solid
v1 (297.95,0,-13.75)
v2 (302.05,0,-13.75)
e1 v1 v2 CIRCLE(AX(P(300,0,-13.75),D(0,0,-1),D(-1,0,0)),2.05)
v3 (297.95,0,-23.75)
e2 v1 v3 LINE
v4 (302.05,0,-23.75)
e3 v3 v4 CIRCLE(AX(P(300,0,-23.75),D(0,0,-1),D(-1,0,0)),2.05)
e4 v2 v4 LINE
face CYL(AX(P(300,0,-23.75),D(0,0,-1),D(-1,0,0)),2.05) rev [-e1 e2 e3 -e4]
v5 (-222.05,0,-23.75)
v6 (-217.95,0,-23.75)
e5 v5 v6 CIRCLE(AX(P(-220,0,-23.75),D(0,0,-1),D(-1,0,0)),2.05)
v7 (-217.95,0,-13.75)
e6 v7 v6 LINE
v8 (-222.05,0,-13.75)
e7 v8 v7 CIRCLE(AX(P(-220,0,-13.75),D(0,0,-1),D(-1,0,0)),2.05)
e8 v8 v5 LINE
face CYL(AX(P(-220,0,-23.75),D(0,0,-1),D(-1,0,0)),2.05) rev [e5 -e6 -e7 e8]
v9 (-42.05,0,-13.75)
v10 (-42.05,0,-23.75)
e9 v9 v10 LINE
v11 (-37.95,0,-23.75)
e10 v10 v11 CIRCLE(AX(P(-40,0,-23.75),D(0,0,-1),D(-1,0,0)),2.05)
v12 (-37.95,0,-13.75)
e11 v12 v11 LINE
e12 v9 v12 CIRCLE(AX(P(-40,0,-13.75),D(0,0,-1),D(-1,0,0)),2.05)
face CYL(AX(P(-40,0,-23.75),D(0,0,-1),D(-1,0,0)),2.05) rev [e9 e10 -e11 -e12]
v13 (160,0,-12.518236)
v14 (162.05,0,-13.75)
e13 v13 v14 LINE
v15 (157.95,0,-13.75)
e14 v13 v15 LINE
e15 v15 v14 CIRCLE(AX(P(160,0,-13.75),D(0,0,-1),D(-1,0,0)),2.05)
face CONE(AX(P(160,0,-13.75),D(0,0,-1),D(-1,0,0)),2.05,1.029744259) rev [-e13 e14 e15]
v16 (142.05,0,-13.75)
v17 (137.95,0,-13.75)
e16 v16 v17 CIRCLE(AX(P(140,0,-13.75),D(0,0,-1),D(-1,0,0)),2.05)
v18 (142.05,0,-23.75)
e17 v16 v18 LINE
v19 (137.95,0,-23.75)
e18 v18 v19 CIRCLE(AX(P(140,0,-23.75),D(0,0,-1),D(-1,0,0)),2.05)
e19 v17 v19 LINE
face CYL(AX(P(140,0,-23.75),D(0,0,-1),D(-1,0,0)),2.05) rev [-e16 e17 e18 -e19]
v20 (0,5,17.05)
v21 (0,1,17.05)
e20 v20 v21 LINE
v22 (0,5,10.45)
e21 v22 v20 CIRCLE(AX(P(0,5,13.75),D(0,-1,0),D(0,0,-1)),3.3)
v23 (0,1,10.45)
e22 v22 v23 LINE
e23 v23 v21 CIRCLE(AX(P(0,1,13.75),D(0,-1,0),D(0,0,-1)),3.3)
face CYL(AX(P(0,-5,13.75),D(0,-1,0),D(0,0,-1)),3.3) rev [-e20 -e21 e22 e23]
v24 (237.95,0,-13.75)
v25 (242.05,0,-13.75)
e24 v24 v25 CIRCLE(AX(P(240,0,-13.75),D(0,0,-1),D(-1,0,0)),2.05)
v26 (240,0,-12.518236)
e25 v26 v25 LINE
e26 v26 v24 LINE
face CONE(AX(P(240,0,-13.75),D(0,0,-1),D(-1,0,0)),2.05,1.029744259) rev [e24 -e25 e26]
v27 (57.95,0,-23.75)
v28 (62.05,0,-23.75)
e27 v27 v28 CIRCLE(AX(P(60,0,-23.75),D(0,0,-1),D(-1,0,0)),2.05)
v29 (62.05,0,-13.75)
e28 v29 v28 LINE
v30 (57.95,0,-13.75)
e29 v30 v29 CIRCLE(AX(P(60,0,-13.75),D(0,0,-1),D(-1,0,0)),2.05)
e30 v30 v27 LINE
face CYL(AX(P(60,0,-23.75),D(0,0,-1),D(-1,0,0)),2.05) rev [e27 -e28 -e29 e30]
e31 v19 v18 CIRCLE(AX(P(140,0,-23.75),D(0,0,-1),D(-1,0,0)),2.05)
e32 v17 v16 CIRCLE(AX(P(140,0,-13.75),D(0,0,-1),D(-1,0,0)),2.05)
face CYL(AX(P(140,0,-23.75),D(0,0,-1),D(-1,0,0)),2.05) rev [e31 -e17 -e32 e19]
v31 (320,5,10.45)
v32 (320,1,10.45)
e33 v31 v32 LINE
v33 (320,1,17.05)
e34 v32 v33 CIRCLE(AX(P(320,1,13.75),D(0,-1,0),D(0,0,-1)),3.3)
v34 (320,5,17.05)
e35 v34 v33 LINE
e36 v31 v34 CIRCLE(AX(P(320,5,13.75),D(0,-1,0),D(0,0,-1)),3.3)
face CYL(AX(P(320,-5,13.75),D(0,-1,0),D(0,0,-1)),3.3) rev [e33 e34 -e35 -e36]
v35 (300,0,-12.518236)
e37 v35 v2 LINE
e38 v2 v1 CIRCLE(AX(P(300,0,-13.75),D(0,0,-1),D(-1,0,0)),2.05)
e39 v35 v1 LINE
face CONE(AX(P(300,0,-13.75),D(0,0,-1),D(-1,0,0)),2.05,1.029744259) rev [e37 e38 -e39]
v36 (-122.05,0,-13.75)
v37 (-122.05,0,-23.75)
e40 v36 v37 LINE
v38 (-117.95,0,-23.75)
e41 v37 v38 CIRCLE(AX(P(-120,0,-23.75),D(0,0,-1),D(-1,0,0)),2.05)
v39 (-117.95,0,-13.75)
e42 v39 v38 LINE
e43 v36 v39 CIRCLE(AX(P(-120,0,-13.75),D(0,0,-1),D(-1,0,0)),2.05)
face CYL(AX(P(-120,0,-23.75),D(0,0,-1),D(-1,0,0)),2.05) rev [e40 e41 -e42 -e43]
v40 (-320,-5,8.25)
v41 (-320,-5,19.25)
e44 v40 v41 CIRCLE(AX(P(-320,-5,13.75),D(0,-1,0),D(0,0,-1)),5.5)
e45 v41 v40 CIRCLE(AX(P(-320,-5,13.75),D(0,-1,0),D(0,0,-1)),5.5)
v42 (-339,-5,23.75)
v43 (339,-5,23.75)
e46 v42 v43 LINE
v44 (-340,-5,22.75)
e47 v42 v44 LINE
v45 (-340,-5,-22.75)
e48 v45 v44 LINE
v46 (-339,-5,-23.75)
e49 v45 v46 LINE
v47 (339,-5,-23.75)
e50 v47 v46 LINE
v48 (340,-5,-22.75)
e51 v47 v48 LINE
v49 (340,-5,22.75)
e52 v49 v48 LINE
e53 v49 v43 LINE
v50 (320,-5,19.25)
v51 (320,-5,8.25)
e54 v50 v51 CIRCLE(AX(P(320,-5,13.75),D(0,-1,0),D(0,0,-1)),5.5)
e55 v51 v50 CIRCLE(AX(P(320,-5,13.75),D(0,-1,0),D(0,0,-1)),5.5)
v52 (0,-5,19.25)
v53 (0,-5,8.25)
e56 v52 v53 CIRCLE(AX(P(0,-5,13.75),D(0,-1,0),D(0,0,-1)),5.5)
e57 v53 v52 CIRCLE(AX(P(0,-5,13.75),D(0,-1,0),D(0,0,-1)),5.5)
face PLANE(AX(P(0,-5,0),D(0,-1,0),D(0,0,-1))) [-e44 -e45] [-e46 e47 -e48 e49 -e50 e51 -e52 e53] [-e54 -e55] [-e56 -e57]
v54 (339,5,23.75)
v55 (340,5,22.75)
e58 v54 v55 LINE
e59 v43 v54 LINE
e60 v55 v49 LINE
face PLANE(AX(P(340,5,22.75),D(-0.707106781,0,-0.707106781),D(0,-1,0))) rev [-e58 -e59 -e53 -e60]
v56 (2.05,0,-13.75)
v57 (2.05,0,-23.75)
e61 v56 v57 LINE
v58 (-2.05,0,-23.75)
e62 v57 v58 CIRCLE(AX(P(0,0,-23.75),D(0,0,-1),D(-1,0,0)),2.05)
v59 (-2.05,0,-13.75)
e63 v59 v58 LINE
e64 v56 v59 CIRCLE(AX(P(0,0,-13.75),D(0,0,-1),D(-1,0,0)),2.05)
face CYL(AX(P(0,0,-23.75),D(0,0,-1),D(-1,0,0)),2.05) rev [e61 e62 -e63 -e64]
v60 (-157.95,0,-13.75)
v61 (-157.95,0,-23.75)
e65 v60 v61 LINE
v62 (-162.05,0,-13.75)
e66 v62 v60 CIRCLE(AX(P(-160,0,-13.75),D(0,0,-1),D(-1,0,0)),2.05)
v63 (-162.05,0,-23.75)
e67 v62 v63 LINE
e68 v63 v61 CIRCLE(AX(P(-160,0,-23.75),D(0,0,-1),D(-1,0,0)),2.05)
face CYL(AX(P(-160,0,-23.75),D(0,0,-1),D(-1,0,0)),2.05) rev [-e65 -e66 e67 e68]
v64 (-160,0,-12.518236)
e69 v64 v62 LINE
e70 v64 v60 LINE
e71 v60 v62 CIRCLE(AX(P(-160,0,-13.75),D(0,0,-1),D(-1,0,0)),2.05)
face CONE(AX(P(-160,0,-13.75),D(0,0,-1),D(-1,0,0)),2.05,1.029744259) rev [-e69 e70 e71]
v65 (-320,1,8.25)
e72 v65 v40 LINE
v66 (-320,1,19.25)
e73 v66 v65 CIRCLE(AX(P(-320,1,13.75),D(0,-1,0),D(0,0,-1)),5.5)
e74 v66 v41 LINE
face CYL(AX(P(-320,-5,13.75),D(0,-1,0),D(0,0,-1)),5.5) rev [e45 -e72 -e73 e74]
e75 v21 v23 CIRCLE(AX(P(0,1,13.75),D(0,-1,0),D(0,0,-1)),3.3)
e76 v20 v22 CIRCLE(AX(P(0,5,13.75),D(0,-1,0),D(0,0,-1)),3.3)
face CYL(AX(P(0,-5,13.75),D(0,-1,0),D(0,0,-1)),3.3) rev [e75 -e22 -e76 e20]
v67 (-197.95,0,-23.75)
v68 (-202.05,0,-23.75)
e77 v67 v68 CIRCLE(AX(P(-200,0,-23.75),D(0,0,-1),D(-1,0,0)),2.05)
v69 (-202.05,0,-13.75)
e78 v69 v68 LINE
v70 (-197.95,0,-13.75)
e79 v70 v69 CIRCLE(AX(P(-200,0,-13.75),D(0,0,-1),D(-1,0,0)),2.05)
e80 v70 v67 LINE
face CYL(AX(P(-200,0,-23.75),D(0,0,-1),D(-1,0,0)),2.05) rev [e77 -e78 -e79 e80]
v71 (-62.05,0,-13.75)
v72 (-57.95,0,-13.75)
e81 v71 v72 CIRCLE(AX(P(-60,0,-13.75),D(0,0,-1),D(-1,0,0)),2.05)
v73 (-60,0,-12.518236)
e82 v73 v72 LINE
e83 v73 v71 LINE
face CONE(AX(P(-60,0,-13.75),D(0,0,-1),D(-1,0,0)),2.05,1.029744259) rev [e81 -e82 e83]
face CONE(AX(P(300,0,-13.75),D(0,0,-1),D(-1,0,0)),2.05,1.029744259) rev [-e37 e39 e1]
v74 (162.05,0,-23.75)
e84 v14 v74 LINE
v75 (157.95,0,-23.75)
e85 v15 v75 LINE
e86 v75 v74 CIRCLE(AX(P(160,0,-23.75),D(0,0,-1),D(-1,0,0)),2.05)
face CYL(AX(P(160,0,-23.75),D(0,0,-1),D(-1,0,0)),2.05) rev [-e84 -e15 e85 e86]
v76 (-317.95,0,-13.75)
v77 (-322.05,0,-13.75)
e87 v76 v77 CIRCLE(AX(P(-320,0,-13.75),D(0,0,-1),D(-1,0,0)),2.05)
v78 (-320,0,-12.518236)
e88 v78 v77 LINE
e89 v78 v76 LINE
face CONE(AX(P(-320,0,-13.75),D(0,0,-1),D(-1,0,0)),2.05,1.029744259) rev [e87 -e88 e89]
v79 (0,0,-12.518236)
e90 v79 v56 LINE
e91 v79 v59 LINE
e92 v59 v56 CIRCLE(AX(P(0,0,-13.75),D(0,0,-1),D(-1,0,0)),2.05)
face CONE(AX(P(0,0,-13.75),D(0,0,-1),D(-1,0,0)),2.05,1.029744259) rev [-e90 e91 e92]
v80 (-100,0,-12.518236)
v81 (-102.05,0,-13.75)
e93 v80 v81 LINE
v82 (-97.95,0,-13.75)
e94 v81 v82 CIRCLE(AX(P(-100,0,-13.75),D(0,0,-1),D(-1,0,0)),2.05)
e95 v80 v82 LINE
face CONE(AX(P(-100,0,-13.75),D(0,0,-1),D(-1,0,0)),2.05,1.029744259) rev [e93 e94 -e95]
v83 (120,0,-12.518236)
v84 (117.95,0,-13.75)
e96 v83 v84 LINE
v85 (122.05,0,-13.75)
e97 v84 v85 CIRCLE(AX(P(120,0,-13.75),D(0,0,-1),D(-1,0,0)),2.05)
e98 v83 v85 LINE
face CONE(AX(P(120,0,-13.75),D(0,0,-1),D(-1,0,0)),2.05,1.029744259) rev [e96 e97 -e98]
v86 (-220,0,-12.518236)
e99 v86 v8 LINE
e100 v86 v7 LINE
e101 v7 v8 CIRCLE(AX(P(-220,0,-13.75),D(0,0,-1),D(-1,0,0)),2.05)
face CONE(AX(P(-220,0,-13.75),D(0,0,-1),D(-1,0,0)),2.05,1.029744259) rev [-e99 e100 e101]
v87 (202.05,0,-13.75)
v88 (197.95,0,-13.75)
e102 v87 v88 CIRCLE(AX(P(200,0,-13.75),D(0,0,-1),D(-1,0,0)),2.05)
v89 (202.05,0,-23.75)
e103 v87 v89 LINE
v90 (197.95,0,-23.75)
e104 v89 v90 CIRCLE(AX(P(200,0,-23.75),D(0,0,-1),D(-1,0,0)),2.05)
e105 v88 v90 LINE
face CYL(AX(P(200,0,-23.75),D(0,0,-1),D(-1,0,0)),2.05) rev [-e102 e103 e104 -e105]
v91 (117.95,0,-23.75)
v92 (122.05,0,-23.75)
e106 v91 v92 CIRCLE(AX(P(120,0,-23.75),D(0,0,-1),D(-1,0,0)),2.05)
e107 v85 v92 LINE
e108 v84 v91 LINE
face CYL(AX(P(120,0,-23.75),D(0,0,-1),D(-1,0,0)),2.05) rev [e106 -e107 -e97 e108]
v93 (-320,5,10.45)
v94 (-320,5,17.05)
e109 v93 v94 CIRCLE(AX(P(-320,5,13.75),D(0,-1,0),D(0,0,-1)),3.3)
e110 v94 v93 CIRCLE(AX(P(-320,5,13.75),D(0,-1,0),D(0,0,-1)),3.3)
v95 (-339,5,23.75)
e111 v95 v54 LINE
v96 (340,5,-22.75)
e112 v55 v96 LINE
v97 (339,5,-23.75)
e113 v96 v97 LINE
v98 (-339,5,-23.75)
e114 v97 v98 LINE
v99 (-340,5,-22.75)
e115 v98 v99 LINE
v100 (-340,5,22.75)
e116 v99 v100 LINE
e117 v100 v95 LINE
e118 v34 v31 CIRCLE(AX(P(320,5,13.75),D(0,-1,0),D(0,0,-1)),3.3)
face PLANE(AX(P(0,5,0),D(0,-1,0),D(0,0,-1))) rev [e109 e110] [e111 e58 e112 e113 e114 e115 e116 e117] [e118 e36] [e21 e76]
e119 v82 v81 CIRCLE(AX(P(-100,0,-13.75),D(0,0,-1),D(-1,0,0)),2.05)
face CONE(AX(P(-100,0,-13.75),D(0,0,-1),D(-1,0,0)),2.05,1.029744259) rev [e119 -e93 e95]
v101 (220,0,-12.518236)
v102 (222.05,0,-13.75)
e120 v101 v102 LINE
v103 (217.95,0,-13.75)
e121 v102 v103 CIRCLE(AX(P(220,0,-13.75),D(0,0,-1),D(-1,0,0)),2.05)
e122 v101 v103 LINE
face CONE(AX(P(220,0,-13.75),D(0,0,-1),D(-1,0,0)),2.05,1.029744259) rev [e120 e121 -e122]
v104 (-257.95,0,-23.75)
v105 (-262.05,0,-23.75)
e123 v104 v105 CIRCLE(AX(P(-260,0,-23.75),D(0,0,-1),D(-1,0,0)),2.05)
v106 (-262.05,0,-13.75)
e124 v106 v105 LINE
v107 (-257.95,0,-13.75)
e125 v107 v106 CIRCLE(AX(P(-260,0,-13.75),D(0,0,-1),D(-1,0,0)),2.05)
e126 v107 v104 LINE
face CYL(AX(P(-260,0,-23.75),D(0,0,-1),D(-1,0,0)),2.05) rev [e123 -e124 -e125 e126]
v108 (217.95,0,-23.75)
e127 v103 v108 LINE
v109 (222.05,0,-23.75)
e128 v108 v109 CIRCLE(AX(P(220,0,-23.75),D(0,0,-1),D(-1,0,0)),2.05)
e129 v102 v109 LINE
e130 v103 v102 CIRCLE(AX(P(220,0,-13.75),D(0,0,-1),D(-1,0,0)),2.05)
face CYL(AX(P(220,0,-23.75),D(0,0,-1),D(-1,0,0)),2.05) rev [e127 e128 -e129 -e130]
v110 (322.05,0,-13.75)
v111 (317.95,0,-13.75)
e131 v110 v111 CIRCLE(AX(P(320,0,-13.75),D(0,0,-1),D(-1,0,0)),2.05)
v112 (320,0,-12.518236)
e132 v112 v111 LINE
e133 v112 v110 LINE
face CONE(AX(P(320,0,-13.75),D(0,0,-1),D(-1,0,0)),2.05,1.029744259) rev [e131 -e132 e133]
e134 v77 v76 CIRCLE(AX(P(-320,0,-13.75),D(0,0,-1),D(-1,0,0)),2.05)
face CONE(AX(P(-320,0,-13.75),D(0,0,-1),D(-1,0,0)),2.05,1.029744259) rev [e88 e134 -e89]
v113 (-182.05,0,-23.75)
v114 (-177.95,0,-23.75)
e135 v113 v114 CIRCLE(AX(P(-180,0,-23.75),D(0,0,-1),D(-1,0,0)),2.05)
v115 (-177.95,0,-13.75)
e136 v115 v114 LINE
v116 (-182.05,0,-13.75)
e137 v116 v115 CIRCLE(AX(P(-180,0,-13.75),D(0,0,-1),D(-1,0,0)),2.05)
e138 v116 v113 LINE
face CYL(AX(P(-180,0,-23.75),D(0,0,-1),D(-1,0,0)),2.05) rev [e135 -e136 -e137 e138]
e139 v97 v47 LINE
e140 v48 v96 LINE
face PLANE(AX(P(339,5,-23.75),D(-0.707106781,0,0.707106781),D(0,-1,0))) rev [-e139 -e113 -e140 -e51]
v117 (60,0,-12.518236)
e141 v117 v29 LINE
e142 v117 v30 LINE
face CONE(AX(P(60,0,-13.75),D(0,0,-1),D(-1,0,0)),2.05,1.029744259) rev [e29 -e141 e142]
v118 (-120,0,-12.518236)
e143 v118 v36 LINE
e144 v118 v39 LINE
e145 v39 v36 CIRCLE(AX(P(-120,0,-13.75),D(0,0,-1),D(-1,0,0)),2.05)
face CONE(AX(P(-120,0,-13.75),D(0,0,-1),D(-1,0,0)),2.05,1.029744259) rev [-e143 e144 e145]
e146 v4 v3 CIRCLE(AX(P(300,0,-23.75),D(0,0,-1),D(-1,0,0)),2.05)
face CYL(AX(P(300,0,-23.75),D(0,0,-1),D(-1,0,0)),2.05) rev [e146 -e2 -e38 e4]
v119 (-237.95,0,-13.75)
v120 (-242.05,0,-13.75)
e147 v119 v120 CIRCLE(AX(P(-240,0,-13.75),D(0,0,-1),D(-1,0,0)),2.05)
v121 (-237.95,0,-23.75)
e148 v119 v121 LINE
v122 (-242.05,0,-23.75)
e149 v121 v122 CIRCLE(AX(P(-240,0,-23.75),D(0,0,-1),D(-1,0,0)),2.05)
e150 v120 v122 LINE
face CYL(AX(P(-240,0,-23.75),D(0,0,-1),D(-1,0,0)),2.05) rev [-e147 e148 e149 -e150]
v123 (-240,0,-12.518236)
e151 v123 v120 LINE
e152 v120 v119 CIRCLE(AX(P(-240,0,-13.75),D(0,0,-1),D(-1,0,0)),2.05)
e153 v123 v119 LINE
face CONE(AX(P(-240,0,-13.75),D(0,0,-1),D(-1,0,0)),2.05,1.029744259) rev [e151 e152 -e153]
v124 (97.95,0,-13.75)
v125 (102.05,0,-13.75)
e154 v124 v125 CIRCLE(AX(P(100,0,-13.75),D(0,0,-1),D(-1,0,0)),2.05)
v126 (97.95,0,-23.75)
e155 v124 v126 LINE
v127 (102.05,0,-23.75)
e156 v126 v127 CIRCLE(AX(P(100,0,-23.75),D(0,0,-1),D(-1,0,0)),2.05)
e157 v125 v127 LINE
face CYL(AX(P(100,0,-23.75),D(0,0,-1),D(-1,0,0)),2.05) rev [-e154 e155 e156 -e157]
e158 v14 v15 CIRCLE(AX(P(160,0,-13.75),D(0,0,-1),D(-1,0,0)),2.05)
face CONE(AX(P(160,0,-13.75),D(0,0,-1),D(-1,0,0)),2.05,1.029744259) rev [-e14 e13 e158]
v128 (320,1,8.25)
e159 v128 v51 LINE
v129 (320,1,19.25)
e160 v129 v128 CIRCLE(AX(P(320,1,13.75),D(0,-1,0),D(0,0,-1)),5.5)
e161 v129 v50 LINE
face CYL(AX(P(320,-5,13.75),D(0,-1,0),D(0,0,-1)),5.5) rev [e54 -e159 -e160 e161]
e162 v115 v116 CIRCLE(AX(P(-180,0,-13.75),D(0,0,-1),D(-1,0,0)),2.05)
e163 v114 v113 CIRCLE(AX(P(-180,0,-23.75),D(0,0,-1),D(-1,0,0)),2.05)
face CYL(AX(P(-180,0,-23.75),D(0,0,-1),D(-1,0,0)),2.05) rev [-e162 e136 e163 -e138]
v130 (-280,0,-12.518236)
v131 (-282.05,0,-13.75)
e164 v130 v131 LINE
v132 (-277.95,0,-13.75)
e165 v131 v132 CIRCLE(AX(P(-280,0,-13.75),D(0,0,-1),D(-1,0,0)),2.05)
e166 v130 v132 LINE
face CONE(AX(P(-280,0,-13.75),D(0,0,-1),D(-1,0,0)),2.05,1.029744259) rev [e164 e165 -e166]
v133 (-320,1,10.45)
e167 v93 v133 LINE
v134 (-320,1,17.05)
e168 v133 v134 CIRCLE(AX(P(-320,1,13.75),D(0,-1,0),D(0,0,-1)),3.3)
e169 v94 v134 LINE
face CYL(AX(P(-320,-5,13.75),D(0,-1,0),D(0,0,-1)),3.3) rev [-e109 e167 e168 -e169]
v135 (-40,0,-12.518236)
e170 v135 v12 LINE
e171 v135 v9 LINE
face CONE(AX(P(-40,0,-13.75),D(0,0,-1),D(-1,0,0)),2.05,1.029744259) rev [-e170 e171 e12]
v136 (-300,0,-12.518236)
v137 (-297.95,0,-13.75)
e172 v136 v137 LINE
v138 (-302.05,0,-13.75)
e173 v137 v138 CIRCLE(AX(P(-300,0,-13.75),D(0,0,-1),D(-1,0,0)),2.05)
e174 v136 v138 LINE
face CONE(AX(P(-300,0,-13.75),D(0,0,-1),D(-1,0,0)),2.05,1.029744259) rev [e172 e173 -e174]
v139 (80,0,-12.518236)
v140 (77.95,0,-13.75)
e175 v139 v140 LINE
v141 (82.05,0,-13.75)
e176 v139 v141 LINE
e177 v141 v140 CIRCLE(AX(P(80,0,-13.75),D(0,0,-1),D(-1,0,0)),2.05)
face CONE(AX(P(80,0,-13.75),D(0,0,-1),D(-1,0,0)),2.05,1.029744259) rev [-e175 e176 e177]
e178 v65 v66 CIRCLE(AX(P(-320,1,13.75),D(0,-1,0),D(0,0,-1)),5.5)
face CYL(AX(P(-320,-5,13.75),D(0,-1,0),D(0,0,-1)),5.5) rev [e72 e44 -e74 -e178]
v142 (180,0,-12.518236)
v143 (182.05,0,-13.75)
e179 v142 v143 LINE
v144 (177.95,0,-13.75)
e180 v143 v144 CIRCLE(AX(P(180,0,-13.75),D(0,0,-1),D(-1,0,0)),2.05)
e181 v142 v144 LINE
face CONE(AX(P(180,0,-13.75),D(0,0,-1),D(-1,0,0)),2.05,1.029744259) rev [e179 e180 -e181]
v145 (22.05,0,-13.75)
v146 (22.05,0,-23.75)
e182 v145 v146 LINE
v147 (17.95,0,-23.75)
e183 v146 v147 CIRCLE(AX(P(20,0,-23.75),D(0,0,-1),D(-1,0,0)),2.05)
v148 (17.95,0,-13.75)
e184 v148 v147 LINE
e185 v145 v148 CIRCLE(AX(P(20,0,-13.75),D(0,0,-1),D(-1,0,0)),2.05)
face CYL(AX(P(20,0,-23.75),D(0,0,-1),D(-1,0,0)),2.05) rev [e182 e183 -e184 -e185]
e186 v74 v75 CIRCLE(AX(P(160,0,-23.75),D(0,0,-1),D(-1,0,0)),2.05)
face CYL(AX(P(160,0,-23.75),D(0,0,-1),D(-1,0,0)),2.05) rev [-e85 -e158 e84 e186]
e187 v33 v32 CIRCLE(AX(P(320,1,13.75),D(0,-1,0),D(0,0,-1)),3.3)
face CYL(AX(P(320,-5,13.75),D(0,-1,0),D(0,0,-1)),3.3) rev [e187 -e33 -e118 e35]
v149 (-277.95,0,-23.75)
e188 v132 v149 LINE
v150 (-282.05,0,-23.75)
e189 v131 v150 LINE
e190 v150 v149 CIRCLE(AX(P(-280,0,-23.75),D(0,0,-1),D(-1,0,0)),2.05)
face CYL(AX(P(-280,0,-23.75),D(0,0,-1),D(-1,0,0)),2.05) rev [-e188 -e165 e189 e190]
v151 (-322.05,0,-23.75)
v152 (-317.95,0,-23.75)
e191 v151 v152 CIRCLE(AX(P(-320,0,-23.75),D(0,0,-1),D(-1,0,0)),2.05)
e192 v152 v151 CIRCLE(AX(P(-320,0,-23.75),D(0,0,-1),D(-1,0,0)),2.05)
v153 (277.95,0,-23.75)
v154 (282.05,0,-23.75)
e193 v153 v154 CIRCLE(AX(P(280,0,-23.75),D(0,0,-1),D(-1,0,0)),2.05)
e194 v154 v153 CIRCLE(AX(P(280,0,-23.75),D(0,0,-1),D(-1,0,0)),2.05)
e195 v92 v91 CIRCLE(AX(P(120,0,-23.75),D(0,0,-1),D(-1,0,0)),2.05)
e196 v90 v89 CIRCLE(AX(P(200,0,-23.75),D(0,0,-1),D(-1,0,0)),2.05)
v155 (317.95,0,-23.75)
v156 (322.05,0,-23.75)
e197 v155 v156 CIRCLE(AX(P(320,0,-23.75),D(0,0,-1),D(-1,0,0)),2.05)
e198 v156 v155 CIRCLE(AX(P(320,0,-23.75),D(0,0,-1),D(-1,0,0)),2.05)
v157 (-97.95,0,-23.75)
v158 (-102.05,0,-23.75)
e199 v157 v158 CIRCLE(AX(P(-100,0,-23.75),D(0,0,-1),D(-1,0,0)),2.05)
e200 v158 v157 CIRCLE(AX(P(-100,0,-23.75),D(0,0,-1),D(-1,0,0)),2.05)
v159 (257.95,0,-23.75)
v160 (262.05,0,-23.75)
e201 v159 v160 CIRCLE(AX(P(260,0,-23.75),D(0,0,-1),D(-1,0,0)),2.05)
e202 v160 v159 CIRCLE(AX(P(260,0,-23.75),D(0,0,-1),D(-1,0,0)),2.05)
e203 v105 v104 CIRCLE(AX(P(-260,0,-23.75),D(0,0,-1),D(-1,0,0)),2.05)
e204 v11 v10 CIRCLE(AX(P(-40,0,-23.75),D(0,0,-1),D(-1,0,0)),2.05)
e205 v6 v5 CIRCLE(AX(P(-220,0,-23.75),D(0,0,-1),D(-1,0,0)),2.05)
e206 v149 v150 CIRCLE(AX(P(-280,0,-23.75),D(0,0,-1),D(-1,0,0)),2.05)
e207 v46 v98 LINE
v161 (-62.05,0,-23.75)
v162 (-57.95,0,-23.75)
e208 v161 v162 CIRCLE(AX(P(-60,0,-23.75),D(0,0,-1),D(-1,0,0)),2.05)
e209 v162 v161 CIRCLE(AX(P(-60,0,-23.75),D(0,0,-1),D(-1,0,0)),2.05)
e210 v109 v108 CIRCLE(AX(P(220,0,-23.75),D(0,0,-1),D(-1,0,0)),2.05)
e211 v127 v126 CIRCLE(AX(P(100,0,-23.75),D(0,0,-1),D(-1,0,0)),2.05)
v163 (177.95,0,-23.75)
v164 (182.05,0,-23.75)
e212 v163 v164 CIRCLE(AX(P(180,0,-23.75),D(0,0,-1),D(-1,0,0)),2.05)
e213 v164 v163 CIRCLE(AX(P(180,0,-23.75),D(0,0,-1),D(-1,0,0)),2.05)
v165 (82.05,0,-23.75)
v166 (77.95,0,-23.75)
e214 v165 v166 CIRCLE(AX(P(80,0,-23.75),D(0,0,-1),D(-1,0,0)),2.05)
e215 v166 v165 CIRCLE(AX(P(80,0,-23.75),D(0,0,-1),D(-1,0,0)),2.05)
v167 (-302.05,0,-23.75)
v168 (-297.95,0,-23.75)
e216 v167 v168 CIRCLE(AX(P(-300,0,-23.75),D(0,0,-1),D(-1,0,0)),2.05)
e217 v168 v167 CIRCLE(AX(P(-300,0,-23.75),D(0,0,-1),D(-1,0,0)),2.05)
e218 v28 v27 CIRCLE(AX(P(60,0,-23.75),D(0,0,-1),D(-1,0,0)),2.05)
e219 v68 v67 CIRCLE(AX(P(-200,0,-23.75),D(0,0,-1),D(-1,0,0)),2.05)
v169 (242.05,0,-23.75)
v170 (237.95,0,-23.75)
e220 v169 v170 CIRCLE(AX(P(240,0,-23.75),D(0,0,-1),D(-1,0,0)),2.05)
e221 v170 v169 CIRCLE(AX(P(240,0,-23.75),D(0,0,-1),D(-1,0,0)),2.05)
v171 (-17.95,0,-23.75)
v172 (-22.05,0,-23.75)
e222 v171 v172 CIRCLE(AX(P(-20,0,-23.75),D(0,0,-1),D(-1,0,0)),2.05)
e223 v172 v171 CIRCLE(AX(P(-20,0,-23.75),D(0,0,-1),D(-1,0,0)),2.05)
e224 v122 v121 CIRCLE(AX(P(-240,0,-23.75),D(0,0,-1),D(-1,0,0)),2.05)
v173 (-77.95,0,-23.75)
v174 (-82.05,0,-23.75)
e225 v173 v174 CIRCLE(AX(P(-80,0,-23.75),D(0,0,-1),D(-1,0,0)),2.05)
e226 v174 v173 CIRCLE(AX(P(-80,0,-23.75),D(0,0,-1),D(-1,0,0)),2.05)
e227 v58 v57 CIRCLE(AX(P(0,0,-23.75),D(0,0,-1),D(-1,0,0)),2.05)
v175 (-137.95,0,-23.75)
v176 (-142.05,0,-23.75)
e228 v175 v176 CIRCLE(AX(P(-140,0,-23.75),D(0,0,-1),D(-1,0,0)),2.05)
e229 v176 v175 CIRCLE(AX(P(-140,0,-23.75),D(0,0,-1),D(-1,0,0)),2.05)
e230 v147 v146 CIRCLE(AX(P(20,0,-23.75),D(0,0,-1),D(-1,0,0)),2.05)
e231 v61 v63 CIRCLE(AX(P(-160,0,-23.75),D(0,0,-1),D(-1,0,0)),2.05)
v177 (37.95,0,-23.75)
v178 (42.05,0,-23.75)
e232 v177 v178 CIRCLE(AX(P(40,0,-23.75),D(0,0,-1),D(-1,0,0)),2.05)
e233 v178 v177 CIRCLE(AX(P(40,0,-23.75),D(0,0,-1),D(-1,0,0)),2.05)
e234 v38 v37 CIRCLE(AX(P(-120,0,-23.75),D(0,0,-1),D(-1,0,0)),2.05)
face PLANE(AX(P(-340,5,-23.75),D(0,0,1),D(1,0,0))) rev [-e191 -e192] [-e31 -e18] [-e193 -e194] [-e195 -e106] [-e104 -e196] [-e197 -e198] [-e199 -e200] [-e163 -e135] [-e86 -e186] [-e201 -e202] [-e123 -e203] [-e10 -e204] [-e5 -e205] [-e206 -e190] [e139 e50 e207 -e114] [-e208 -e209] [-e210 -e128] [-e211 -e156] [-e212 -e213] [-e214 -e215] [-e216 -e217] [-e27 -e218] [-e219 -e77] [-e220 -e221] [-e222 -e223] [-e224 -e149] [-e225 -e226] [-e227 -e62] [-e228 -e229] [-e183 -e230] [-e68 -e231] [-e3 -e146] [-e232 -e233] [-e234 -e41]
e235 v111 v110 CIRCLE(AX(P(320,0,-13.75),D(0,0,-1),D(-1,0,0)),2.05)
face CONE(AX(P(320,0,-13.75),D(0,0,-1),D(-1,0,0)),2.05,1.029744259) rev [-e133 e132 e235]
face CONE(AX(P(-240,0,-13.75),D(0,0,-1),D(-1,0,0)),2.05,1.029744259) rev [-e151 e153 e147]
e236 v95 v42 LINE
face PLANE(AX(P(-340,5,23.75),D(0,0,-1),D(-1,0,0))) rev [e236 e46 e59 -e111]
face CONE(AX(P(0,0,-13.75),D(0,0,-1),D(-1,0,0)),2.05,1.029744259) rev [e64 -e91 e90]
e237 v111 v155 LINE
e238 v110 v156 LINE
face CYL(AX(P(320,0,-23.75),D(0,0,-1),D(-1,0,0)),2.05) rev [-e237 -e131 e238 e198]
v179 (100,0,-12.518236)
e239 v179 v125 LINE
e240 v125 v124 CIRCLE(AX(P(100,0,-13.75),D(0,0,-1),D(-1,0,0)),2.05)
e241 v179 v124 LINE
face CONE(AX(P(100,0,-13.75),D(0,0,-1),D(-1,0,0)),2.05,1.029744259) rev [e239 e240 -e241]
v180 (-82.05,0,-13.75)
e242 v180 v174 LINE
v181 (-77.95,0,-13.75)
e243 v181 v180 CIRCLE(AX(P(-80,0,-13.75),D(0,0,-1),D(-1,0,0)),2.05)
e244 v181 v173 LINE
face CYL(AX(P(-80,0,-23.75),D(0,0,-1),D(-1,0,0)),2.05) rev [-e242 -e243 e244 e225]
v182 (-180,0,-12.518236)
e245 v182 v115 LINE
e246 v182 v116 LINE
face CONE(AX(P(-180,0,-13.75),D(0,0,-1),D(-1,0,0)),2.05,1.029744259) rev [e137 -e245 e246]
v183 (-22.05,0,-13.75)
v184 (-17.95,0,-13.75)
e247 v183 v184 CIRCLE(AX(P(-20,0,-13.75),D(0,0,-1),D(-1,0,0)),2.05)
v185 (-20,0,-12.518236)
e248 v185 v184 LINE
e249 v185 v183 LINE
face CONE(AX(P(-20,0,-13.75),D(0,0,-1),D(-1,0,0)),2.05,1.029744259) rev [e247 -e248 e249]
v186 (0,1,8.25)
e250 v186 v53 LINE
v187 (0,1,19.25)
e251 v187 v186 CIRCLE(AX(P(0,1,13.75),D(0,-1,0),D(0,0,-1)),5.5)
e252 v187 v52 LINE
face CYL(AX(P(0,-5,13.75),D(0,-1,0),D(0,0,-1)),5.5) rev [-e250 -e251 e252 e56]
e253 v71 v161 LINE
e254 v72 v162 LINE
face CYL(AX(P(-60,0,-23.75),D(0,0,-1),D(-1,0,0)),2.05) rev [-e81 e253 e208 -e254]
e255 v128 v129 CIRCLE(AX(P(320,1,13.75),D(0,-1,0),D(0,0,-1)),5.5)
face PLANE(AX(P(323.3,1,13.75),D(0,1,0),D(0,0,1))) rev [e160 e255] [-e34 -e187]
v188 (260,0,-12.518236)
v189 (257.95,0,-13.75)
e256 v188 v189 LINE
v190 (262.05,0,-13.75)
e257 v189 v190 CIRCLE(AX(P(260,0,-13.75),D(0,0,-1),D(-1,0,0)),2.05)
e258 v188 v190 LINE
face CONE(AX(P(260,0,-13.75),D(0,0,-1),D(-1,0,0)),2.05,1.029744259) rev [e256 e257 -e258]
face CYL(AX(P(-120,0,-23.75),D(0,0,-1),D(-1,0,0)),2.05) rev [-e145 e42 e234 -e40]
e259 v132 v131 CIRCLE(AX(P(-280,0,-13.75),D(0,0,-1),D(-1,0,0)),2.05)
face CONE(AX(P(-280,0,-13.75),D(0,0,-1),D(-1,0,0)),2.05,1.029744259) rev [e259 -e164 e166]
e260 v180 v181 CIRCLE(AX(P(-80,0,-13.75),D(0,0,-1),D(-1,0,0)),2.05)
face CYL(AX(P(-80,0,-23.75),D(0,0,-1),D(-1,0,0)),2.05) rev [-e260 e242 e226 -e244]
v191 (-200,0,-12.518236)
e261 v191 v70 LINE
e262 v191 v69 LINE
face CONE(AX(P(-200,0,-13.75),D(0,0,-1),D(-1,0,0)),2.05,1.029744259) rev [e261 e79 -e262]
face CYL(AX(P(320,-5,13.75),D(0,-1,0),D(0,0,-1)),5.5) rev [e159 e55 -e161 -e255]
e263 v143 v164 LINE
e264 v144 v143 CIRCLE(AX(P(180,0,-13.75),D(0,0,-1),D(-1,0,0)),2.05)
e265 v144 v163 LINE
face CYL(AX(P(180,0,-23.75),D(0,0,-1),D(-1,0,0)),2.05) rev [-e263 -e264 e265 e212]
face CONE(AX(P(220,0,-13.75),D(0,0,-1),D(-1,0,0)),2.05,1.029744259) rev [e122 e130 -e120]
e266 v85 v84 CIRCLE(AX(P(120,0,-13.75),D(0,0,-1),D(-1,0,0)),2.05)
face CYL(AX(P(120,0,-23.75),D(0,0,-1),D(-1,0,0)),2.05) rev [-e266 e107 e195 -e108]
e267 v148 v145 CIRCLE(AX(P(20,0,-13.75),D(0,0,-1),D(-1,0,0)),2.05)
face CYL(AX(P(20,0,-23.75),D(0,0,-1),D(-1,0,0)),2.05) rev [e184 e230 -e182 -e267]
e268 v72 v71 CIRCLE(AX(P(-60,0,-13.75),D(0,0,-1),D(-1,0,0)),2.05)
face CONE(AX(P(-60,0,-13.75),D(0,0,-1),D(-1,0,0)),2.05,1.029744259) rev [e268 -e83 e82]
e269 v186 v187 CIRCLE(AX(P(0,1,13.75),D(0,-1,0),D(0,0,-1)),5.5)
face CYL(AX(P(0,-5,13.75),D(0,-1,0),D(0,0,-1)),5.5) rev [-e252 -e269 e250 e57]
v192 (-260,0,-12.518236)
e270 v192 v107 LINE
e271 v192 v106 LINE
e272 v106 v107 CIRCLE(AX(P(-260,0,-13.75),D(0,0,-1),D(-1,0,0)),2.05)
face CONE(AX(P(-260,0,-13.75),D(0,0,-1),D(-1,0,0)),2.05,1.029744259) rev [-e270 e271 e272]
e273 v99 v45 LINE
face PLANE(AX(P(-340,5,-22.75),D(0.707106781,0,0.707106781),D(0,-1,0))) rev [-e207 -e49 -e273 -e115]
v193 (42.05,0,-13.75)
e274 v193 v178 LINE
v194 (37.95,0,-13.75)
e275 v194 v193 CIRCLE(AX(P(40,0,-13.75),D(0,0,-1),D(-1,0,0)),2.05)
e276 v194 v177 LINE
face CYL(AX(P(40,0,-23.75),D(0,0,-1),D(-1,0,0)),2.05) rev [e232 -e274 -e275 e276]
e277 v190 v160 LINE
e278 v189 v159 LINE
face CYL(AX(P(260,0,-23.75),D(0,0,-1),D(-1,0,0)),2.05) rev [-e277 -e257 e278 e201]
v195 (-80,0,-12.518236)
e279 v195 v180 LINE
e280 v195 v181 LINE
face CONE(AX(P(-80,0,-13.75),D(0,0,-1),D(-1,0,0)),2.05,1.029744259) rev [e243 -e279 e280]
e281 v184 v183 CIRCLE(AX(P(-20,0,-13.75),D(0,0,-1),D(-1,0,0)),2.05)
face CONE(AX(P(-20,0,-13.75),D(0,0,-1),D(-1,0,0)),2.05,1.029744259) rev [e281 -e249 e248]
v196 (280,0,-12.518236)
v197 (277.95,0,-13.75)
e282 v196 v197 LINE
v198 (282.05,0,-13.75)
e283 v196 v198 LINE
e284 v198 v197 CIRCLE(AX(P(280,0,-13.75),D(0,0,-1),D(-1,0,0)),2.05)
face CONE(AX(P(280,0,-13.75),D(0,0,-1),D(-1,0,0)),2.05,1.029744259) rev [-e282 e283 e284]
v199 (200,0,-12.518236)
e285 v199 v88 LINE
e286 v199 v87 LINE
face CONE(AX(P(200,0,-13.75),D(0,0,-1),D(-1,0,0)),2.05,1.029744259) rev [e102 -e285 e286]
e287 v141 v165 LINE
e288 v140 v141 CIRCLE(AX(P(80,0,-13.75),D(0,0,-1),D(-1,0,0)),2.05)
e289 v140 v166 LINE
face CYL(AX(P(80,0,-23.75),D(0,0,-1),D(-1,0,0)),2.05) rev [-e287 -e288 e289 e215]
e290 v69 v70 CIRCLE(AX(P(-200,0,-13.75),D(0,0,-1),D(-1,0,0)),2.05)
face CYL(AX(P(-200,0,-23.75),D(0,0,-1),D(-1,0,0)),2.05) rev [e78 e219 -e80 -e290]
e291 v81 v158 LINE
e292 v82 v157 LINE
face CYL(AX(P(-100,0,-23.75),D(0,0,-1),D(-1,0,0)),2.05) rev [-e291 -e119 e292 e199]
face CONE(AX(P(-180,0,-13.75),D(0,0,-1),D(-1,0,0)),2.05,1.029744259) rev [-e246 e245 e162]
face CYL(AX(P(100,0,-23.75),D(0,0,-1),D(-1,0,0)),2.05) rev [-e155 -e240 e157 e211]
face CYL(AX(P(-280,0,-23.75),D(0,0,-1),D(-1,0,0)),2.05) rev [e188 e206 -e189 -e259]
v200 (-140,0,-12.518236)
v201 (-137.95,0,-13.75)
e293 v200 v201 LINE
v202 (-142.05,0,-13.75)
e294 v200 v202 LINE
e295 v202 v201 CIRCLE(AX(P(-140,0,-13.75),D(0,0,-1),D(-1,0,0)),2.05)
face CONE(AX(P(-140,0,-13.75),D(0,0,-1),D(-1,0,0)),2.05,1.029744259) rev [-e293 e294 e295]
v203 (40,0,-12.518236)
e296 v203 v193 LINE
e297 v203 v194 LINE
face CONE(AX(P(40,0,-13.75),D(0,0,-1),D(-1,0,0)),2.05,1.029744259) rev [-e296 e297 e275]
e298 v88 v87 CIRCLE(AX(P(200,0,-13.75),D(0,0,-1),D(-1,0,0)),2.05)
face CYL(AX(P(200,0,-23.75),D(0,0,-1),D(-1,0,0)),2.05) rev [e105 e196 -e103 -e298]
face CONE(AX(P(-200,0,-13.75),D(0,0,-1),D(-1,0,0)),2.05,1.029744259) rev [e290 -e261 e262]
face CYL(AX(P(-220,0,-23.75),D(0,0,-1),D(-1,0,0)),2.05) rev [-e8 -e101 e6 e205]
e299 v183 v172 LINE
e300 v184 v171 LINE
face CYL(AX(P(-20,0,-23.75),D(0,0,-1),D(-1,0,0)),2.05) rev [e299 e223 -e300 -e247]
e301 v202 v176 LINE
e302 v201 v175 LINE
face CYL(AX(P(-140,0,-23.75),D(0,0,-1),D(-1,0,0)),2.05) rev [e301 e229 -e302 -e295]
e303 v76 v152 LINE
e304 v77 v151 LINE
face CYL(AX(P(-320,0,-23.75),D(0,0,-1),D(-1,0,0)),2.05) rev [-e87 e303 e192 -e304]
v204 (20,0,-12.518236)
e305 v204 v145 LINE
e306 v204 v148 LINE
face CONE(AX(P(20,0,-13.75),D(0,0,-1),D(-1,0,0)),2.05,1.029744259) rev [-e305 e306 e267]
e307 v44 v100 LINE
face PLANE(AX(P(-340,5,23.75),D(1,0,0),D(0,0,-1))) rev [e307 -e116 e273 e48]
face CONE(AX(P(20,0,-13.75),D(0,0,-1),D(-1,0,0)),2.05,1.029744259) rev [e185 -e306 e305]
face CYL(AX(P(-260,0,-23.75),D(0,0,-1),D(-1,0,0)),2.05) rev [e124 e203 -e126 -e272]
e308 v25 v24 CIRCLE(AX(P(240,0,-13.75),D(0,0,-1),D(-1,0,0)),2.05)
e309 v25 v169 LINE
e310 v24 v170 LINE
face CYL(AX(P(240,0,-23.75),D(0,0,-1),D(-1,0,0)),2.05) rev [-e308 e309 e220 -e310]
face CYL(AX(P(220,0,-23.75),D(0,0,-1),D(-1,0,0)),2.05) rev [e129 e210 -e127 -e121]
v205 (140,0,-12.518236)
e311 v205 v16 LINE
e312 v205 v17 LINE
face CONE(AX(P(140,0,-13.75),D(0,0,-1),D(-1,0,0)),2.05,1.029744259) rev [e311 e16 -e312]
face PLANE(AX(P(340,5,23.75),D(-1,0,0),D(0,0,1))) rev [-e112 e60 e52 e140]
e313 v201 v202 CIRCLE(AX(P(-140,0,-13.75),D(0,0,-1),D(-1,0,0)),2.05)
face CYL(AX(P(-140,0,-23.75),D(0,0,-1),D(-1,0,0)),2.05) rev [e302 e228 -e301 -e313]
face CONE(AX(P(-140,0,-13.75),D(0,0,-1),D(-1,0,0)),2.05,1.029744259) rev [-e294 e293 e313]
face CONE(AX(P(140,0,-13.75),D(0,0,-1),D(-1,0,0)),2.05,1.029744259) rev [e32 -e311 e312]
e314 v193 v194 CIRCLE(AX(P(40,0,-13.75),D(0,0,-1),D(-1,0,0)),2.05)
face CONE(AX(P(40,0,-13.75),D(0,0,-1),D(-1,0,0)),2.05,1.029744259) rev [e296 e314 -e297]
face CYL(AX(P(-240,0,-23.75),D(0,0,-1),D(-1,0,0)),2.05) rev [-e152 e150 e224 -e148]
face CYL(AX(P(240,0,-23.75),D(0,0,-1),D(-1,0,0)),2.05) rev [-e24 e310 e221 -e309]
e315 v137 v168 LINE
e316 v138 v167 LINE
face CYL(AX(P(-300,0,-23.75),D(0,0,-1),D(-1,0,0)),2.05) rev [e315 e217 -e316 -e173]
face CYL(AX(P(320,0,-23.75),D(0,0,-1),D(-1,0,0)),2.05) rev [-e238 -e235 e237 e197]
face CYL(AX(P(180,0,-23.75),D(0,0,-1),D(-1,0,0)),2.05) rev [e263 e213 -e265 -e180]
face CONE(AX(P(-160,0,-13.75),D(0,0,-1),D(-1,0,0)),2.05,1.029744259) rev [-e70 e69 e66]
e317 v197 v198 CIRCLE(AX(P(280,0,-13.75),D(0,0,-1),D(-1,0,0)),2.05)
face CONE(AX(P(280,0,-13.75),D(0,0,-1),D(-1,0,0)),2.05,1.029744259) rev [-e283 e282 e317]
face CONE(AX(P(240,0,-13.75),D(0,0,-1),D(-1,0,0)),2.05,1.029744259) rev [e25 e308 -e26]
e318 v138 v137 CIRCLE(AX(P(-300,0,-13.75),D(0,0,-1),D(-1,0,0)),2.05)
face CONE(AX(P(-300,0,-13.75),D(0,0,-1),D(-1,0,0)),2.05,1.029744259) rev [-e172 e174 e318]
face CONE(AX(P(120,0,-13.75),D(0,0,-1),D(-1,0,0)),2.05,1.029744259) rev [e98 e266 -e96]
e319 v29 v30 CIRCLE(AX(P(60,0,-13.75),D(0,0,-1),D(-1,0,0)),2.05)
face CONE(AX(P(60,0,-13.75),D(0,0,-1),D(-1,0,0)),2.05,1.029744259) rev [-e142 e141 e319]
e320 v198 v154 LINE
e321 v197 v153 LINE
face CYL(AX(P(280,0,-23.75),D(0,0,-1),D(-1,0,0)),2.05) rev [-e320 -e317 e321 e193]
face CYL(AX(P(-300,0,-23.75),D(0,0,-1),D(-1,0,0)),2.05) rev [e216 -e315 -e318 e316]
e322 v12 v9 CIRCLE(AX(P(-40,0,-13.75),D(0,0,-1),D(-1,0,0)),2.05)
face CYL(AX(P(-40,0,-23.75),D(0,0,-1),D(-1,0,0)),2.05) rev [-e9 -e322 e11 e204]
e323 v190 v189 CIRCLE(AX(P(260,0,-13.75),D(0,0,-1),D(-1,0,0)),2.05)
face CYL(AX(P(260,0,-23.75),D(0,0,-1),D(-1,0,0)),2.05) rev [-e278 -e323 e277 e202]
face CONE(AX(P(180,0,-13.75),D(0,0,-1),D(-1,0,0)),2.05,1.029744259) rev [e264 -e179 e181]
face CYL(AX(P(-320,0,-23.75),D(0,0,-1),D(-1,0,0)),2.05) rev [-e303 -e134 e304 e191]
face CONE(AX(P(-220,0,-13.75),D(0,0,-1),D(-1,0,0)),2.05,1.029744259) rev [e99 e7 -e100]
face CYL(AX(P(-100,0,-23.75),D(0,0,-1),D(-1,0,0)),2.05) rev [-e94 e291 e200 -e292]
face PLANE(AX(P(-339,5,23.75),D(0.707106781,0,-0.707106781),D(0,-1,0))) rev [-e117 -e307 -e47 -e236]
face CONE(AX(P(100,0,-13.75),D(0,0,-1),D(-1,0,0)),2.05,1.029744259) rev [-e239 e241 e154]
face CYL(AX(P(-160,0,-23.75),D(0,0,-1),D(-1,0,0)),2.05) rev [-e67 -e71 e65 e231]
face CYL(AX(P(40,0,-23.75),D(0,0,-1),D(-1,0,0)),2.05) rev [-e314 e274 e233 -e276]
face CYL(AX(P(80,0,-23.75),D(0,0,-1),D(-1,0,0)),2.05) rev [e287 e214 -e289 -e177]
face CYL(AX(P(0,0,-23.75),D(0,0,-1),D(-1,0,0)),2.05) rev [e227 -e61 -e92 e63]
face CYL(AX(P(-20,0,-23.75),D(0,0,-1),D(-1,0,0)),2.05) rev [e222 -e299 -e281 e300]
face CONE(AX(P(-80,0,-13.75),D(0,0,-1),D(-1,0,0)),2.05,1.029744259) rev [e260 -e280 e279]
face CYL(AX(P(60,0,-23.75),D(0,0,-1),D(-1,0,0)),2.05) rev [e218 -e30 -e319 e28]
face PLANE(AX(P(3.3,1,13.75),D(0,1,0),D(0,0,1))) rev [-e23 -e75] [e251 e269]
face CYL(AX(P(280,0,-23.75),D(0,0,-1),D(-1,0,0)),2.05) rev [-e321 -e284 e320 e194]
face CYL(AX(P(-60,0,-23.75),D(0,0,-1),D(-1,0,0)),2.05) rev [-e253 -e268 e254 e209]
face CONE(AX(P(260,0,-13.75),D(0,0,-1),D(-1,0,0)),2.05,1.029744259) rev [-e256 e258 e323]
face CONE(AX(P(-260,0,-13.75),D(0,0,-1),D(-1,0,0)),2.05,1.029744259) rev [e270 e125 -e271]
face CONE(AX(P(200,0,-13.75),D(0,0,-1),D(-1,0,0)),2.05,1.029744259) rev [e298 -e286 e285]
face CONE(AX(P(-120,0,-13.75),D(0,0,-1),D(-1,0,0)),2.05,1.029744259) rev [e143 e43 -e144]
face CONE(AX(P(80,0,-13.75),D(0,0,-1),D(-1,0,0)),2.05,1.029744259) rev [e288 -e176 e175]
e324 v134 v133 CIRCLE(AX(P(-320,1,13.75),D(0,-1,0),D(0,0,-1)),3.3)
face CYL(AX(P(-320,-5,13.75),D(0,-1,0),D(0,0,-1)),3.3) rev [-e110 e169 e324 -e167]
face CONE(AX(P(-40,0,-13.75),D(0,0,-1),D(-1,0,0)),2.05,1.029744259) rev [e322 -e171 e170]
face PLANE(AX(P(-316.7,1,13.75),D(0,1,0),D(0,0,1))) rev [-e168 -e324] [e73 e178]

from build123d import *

# Parameters (mm, degrees)
SKETCH_1_W                  = 680
SKETCH_1_H                  = 47.5
EXTRUDE_1_DEPTH             = 5
CHAMFER_1_SIZE              = 1
HOLE_WIZARD_1_D             = 6.6
HOLE_WIZARD_1_CBORE_D       = 11
HOLE_WIZARD_1_CBORE_DEPTH   = 6
HOLE_WIZARD_4_1_4_1_1_D     = 4.1
HOLE_WIZARD_4_1_4_1_1_DEPTH = 10
HOLE_WIZARD_4_1_4_1_1_TIP   = 1.231764269


with BuildPart() as part:
    # 草图1 → 凸台-拉伸1 (new, symmetric)
    with BuildSketch(Plane(origin=(0, 0, 0), x_dir=(1, 0, 0), z_dir=(0, 1, 0))):
        Rectangle(SKETCH_1_W, SKETCH_1_H)
    extrude(amount=EXTRUDE_1_DEPTH, both=True)

    # 倒角1
    chamfer_1_edges = [part.edges().sort_by_distance(p)[0] for p in [
        (340, 0, 23.75),
        (-340, 0, 23.75),
        (-340, 0, -23.75),
        (340, 0, -23.75),
    ]]
    chamfer(chamfer_1_edges, length=CHAMFER_1_SIZE)

    # 打孔尺寸(%根据)内六角圆柱头螺钉的类型1 (through all)
    with Locations(Plane(origin=(0, -5, 0), x_dir=(-1, 0, 0), z_dir=(0, -1, 0))):
        with Locations((-320, -13.75), (0, -13.75), (320, -13.75)):
            CounterBoreHole(HOLE_WIZARD_1_D / 2, HOLE_WIZARD_1_CBORE_D / 2, HOLE_WIZARD_1_CBORE_DEPTH)

    # Ø4.1 (4.1) 直径孔1
    with Locations(Plane(origin=(0, 0, -23.75), x_dir=(-1, 0, 0), z_dir=(0, 0, -1))):
        with Locations((-320, 0), (-300, 0), (-280, 0), (-260, 0), (-240, 0), (-220, 0), (-200, 0), (-180, 0), (-160, 0), (-140, 0), (-120, 0), (-100, 0), (-80, 0), (-60, 0), (-40, 0), (-20, 0), (0, 0), (20, 0), (40, 0), (60, 0), (80, 0), (100, 0), (120, 0), (140, 0), (160, 0), (180, 0), (200, 0), (220, 0), (240, 0), (260, 0), (280, 0), (300, 0), (320, 0)):
            Hole(HOLE_WIZARD_4_1_4_1_1_D / 2, depth=HOLE_WIZARD_4_1_4_1_1_DEPTH)
            with Locations((0, 0, -(HOLE_WIZARD_4_1_4_1_1_DEPTH + HOLE_WIZARD_4_1_4_1_1_TIP / 2))):  # 118° drill point
                Cone(0, HOLE_WIZARD_4_1_4_1_1_D / 2, HOLE_WIZARD_4_1_4_1_1_TIP, mode=Mode.SUBTRACT)


solid = part.part
